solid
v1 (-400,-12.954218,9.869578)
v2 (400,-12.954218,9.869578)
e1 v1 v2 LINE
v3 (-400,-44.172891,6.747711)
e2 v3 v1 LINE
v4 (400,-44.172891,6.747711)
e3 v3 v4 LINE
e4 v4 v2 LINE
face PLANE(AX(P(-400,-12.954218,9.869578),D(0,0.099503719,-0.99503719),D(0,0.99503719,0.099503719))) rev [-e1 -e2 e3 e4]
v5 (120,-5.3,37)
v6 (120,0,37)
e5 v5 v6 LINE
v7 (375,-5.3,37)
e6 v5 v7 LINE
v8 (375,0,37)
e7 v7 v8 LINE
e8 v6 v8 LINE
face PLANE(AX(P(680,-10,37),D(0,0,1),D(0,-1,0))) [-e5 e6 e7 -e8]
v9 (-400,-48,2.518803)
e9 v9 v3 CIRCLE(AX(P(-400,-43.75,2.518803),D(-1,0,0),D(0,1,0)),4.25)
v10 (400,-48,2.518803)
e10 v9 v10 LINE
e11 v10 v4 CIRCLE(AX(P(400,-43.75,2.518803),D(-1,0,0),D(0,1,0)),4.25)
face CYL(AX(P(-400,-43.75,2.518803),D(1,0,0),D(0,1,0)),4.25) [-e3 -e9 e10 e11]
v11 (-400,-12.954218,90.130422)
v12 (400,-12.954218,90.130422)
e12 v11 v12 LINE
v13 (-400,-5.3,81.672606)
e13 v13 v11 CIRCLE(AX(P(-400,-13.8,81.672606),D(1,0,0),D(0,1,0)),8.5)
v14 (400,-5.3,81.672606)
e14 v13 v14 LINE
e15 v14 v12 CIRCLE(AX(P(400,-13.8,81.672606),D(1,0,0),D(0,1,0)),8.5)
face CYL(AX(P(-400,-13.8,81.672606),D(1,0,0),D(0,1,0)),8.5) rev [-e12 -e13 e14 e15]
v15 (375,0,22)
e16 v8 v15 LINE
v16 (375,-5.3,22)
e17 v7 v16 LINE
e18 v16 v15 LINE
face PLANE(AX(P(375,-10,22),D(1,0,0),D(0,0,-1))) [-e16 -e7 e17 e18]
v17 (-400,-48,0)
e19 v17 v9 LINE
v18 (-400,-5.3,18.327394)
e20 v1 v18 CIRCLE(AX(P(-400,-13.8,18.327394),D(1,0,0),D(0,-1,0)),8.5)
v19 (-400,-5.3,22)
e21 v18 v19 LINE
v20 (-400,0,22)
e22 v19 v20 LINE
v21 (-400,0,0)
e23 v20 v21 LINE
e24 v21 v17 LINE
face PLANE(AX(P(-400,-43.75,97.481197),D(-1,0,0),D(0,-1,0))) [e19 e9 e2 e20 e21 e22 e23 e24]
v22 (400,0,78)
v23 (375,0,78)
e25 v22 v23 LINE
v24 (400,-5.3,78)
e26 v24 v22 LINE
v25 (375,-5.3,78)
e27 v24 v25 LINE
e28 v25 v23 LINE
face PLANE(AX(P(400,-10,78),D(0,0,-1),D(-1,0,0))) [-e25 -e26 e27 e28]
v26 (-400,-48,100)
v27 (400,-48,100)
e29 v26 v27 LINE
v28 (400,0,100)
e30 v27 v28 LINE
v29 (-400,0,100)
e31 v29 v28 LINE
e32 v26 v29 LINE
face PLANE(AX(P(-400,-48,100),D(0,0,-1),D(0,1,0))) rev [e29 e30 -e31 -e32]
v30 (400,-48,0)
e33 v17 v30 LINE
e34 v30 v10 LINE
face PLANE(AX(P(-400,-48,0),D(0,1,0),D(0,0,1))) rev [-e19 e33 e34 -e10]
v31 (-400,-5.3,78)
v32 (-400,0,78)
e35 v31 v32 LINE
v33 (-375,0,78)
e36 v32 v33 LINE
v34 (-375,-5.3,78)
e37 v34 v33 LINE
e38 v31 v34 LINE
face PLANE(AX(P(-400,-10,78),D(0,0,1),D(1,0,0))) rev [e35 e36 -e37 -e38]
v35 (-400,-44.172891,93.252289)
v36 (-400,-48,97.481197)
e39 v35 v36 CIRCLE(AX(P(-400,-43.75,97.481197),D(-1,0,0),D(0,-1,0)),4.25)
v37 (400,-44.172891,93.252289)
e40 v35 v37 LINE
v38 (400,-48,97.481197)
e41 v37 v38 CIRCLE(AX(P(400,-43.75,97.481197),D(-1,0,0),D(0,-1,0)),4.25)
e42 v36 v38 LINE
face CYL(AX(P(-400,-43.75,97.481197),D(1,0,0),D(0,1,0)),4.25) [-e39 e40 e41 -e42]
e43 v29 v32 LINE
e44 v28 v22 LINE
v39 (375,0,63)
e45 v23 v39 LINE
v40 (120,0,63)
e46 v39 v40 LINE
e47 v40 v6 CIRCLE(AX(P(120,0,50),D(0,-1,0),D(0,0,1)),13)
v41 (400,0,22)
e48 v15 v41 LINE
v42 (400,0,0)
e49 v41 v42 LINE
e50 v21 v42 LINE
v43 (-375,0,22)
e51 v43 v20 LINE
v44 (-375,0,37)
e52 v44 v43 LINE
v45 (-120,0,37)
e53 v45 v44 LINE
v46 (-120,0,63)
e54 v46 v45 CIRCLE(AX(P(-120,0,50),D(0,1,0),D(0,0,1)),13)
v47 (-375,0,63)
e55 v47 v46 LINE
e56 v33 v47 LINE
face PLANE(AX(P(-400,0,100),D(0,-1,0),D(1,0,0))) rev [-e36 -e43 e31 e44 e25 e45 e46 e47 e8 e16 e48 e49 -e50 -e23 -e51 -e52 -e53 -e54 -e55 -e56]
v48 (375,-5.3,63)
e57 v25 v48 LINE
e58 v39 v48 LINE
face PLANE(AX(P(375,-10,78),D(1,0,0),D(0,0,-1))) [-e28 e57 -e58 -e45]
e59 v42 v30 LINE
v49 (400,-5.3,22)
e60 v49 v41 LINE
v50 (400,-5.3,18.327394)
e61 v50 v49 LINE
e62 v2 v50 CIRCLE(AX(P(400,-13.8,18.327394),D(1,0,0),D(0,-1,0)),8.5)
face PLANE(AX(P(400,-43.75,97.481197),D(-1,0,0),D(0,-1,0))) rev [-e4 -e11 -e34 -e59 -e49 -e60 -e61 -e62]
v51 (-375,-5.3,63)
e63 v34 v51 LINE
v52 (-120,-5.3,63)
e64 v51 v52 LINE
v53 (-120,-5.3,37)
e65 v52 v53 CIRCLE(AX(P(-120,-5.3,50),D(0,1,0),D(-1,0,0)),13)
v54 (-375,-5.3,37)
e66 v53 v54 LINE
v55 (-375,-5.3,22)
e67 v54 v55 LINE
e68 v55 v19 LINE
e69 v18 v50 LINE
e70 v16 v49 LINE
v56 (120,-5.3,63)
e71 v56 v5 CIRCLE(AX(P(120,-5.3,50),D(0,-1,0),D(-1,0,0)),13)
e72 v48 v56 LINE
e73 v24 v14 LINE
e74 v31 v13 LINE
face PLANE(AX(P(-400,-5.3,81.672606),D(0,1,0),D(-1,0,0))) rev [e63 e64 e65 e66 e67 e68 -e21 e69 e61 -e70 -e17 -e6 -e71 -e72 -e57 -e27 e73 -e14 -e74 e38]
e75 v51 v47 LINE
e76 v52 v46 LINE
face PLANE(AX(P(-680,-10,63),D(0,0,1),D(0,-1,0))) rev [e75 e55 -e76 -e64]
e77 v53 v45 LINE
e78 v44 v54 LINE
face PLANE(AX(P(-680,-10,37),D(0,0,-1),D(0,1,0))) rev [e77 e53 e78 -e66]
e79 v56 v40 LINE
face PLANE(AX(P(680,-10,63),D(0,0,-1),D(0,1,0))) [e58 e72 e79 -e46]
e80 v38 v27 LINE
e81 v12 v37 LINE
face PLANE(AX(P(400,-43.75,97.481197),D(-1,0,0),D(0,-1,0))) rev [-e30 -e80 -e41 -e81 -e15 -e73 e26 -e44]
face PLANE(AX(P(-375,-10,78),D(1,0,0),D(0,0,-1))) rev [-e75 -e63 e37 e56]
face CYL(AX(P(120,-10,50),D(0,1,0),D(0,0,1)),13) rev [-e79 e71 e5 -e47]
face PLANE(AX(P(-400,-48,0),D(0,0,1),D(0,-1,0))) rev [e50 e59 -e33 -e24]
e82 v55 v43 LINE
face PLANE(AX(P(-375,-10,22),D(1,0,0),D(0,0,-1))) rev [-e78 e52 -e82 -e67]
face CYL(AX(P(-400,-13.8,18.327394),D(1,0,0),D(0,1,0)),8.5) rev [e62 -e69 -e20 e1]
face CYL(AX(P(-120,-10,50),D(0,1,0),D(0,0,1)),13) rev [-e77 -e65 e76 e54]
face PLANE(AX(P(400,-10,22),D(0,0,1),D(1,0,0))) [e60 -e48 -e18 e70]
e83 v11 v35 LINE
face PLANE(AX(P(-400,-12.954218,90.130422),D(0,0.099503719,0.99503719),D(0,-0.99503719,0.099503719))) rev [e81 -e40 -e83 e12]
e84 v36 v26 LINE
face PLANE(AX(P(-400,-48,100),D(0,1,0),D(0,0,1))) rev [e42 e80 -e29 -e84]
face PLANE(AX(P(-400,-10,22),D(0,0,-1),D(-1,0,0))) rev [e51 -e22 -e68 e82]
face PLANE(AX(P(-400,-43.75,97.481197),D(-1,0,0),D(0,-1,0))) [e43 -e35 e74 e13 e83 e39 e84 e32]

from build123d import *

# Parameters (mm, degrees)
HOT_ROLLED_CHANNEL_STEEL_GB_T_707_1988_DEPTH = 800
CUT_EXTRUDE1_DEPTH                           = 10
SKETCH4_W                                    = 25
SKETCH4_H                                    = 15
CUT_EXTRUDE2_DEPTH                           = 10


with BuildPart() as part:
    # Sketch1 → hot-rolled channel steel (GB/T 707-1988) 10(1) (new body)
    with BuildSketch(Plane(origin=(400, 0, 0), x_dir=(0, -1, 0), z_dir=(-1, 0, 0))):
        with BuildLine():
            Line((48, 100), (0, 100))
            Line((0, 100), (0, 0))
            Line((0, 0), (48, 0))
            Line((48, 0), (48, 2.518802861))
            ThreePointArc((48, 2.518802861), (46.901173268, 5.370575474), (44.172890806, 6.747710919))
            Line((44.172890806, 6.747710919), (12.954218388, 9.869578161))
            ThreePointArc((12.954218388, 9.869578161), (7.497653465, 12.623849051), (5.3, 18.327394278))
            Line((5.3, 18.327394278), (5.3, 81.672605722))
            ThreePointArc((5.3, 81.672605722), (7.497653465, 87.376150949), (12.954218388, 90.130421839))
            Line((12.954218388, 90.130421839), (44.172890806, 93.252289081))
            ThreePointArc((44.172890806, 93.252289081), (46.901173268, 94.629424526), (48, 97.481197139))
            Line((48, 97.481197139), (48, 100))
        make_face()
    extrude(amount=HOT_ROLLED_CHANNEL_STEEL_GB_T_707_1988_DEPTH)

    # Sketch3 → Cut-Extrude1 (cut)
    with BuildSketch(Plane(origin=(0, 0, 0), x_dir=(1, 0, 0), z_dir=(0, 1, 0))):
        with BuildLine():
            Line((-680, -37), (-120, -37))
            ThreePointArc((-120, -37), (-107, -50), (-120, -63))
            Line((-120, -63), (-680, -63))
            ThreePointArc((-680, -63), (-693, -50), (-680, -37))
        make_face()
    cut_extrude1 = extrude(amount=-CUT_EXTRUDE1_DEPTH, mode=Mode.SUBTRACT)

    # Sketch4 → Cut-Extrude2 (cut)
    with BuildSketch(Plane(origin=(0, 0, 0), x_dir=(1, 0, 0), z_dir=(0, 1, 0))):
        with Locations((-387.5, -29.5)):
            Rectangle(SKETCH4_W, SKETCH4_H)
        with Locations((-387.5, -70.5)):
            Rectangle(SKETCH4_W, SKETCH4_H)
    cut_extrude2 = extrude(amount=-CUT_EXTRUDE2_DEPTH, mode=Mode.SUBTRACT)

    # Mirror1: Cut-Extrude1, Cut-Extrude2 across plane
    add(cut_extrude1.mirror(Plane(origin=(0, 0, 0), x_dir=(0, 0, 1), z_dir=(1, 0, 0))), mode=Mode.SUBTRACT)
    add(cut_extrude2.mirror(Plane(origin=(0, 0, 0), x_dir=(0, 0, 1), z_dir=(1, 0, 0))), mode=Mode.SUBTRACT)


solid = part.part
